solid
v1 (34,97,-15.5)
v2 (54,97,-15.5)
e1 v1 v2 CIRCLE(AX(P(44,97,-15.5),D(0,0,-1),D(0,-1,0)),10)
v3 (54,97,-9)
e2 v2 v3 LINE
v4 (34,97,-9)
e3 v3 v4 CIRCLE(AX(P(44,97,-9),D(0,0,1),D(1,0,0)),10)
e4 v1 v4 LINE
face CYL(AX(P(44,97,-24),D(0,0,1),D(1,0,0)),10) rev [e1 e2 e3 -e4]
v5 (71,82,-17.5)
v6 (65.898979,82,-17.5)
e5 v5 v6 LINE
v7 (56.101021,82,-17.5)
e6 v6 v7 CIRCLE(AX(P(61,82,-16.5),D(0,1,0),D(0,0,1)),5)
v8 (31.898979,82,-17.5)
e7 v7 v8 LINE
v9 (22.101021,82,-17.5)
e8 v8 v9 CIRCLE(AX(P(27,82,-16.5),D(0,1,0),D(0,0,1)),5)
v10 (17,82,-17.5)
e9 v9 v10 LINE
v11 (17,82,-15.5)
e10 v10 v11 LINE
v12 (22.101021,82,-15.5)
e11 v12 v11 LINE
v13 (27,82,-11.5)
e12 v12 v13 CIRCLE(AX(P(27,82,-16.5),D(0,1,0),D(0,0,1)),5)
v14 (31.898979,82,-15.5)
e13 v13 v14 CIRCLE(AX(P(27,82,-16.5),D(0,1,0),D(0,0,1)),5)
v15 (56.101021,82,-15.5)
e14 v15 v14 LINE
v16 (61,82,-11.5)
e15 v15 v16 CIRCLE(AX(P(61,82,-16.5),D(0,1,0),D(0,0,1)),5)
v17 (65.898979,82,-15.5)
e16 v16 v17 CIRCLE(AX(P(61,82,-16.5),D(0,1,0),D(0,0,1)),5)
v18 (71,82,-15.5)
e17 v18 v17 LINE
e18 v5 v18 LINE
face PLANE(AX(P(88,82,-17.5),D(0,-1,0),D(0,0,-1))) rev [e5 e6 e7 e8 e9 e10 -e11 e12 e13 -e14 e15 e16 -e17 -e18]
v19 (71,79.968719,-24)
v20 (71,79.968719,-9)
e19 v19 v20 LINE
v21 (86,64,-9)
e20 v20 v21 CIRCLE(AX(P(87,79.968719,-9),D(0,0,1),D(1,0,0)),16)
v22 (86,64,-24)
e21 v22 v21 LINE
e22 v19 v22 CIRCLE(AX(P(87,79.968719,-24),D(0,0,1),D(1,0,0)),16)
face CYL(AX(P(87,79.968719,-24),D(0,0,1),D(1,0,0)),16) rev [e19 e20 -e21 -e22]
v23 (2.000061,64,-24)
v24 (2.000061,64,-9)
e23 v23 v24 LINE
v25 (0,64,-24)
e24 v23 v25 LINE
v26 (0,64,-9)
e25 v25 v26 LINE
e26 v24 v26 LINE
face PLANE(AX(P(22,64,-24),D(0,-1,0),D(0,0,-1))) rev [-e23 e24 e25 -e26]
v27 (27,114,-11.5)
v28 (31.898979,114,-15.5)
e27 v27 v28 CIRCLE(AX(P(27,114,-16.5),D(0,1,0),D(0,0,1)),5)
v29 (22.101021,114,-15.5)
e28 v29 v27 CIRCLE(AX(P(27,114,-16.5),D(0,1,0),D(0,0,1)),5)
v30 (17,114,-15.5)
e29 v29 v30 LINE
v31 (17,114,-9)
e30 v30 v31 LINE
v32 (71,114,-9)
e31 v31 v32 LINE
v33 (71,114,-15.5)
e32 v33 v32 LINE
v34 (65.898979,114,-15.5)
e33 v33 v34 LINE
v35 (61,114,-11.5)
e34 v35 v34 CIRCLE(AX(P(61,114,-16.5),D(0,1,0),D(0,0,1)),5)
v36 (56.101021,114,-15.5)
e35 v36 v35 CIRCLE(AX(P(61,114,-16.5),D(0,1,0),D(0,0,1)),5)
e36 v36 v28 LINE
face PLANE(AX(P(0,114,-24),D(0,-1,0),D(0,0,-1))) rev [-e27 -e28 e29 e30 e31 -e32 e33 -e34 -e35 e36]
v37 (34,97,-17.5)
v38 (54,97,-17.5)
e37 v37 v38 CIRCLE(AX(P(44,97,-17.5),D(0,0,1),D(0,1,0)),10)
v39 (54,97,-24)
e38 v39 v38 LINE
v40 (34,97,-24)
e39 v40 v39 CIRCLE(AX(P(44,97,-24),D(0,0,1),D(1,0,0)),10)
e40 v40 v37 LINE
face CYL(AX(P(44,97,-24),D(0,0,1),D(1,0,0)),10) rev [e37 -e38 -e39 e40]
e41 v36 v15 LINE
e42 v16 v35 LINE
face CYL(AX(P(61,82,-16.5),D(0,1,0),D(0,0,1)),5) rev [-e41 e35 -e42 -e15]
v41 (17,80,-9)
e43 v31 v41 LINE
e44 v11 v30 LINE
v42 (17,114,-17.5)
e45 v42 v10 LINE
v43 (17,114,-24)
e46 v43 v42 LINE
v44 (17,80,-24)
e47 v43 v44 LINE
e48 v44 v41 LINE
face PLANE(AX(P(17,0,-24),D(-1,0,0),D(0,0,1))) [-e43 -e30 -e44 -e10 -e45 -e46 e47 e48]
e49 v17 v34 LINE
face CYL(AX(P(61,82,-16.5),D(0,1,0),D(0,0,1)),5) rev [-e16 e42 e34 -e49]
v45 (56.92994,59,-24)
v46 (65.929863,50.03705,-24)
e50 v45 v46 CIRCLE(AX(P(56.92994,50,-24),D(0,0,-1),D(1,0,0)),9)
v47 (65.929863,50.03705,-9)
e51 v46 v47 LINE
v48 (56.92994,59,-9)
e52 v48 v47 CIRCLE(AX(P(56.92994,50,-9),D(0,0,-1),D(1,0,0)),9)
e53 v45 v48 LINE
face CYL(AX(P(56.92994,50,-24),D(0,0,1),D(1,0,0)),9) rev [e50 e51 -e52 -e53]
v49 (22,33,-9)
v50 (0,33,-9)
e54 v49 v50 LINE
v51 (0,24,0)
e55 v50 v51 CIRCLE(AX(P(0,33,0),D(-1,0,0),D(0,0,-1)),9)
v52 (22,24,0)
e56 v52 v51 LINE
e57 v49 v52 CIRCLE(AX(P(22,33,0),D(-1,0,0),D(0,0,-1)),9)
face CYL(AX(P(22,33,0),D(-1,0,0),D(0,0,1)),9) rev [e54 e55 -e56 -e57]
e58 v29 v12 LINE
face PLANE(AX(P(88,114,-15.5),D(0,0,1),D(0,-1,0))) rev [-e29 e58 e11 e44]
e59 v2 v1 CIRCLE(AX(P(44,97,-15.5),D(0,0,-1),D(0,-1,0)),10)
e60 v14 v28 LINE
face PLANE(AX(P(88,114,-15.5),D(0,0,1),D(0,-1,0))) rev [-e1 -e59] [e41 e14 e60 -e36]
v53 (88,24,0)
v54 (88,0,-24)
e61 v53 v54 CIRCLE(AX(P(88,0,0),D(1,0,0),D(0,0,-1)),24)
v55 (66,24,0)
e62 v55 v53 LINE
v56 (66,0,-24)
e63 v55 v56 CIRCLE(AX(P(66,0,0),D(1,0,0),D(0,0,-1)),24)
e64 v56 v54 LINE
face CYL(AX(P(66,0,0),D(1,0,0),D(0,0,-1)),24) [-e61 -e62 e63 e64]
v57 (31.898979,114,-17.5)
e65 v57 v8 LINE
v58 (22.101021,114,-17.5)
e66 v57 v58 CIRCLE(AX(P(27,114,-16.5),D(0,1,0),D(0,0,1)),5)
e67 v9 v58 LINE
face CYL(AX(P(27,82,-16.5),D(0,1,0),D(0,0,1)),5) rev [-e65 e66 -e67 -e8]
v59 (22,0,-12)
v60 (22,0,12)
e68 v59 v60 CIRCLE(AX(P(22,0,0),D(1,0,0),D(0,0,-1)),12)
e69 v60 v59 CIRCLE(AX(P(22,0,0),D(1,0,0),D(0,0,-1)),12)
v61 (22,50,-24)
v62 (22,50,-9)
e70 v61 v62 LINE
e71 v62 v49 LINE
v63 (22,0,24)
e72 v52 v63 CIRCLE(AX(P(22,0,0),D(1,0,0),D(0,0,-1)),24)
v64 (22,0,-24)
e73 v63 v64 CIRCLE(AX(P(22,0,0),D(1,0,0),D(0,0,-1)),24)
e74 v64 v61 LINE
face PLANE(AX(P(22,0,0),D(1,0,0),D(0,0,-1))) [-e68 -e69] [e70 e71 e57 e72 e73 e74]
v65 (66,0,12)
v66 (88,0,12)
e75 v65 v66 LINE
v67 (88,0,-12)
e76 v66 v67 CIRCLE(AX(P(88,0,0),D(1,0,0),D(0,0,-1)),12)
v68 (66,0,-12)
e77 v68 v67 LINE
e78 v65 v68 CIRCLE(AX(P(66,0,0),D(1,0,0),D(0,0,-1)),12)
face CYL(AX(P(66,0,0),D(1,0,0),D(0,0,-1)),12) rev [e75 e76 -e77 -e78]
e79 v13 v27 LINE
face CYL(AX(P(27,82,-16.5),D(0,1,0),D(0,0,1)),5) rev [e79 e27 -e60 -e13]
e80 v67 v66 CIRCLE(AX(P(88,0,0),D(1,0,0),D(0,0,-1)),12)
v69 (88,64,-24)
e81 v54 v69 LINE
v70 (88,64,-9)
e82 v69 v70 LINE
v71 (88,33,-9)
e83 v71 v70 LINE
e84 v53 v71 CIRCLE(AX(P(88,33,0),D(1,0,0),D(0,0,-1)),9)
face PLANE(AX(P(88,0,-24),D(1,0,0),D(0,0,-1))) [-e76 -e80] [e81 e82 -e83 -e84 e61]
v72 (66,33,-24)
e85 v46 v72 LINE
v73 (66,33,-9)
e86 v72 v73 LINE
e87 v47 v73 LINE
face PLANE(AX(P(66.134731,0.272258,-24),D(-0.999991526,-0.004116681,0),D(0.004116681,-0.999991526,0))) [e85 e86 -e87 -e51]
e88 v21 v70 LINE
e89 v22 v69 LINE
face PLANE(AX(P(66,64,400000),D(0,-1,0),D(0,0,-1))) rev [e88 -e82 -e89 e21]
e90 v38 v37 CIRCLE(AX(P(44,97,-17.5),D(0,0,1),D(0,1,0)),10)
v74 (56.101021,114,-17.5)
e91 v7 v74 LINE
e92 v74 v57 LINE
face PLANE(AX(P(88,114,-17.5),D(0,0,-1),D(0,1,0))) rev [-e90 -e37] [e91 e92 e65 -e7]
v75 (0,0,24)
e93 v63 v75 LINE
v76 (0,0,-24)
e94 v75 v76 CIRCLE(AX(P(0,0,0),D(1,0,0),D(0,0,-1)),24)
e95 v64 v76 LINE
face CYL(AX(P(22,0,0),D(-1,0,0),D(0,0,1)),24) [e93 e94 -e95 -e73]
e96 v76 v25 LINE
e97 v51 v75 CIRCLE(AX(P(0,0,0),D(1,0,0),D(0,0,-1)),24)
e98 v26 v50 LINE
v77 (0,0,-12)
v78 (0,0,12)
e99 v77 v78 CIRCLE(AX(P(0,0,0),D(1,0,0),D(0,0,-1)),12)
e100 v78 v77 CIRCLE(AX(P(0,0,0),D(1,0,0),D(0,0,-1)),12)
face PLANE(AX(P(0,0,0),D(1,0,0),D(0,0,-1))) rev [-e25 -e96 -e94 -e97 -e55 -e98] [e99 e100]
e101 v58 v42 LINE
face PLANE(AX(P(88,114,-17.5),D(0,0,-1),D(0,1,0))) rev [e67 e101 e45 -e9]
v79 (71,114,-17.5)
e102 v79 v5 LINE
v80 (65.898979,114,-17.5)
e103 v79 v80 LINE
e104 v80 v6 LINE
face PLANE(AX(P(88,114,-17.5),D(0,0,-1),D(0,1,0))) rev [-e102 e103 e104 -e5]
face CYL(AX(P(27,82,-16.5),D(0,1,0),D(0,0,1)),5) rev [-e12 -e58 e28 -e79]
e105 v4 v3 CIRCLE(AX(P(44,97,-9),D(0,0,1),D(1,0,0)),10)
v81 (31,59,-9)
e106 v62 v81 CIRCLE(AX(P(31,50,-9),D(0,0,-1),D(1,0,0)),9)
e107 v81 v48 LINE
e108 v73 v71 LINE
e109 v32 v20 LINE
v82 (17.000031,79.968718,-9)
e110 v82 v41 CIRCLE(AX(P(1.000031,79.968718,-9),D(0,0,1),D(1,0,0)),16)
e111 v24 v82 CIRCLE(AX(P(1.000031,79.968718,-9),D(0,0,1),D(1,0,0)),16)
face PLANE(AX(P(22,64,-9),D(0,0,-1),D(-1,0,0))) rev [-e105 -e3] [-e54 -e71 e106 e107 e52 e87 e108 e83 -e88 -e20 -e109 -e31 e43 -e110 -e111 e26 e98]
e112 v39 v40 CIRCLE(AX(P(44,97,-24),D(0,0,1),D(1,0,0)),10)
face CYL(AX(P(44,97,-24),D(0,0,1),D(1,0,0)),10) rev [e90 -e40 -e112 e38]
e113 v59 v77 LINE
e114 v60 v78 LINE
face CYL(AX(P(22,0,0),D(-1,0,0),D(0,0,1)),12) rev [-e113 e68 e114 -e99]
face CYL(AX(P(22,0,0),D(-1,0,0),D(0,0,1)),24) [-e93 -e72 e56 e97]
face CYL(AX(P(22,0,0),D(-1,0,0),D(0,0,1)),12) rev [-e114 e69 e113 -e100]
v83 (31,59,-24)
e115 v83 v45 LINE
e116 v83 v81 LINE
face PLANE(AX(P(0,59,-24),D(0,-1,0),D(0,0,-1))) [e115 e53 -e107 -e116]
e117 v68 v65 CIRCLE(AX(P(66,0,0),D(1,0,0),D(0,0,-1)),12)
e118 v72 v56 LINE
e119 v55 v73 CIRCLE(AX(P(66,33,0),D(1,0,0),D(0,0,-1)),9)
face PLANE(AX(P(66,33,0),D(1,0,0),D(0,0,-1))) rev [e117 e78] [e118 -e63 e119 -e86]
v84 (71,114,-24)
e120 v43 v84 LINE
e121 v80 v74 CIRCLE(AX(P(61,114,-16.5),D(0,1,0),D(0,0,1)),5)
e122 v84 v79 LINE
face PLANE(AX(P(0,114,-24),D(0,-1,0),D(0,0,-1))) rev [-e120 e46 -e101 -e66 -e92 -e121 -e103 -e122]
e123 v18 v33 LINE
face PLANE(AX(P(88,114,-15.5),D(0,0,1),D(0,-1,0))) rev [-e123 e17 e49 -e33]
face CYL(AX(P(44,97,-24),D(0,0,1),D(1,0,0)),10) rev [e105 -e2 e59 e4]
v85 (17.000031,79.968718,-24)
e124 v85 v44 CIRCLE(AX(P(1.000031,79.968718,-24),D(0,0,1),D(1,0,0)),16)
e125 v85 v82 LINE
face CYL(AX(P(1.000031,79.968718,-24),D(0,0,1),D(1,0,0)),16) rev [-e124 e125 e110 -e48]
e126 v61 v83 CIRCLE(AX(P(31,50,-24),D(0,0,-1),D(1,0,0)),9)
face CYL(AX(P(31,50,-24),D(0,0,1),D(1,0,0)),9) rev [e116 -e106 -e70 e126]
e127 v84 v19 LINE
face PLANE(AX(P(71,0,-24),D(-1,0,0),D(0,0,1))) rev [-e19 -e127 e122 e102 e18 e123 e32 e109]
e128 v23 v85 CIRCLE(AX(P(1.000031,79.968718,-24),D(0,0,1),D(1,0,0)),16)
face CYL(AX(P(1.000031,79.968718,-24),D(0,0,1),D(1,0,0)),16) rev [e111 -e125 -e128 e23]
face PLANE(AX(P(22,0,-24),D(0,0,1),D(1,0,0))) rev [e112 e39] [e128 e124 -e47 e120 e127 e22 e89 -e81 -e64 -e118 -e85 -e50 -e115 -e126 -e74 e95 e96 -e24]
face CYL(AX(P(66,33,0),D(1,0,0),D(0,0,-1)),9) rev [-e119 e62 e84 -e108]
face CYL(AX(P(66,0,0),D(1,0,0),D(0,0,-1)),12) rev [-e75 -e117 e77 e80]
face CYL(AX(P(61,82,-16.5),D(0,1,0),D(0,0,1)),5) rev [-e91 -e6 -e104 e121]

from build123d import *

# Parameters (mm, degrees)
FORK_EYE_PROFILE_R         = 12
FORK_LEG_LEFT_DEPTH        = 22
FORK_START                 = 88
SKETCH1_4_R                = 12
FORK_LEG_RIGHT_DEPTH       = 22
CLAMP_BLOCK_DEPTH          = 15
CROSS_HOLE_SKETCH_R        = 10
CROSS_HOLE_DEPTH           = 15
CLAMP_SLIT_SKETCH_W        = 2
CLAMP_SLIT_SKETCH_H        = 32
CLAMP_SLIT_DEPTH           = 137.429468957
CLAMP_SCREW_HOLES_SKETCH_R = 5
CLAMP_SCREW_HOLES_DEPTH    = 32


with BuildPart() as part:
    # Fork Eye Profile → Fork Leg Left (new body)
    with BuildSketch(Plane(origin=(0, 0, 0), x_dir=(0, 0, -1), z_dir=(1, 0, 0))):
        with BuildLine():
            Line((24, 0), (24, 64))
            Line((24, 64), (9, 64))
            Line((9, 64), (9, 33))
            ThreePointArc((9, 33), (6.363961031, 26.636038969), (0, 24))
            ThreePointArc((0, 24), (-16.970562748, -16.970562748), (24, 0))
        make_face()
        Circle(FORK_EYE_PROFILE_R, mode=Mode.SUBTRACT)
    extrude(amount=FORK_LEG_LEFT_DEPTH)



with BuildPart() as body_2:
    # Sketch1_4 → Fork Leg Right (new body)
    with BuildSketch(Plane(origin=(0, 0, 0), x_dir=(0, 0, -1), z_dir=(1, 0, 0)).offset(FORK_START)):
        with BuildLine():
            Line((24, 0), (24, 64))
            Line((24, 64), (9, 64))
            Line((9, 64), (9, 33))
            ThreePointArc((9, 33), (6.363961031, 26.636038969), (0, 24))
            ThreePointArc((0, 24), (-16.970562748, -16.970562748), (24, 0))
        make_face()
        Circle(SKETCH1_4_R, mode=Mode.SUBTRACT)
    extrude(amount=-FORK_LEG_RIGHT_DEPTH)


with BuildPart() as part_1:
    add(part.part)

    add(body_2.part)  # Clamp Block merges body 2
    # Clamp Block Profile → Clamp Block (add)
    with BuildSketch(Plane.XY.offset(-9)):
        with BuildLine():
            Line((71, 114), (17, 114))
            Line((17, 114), (17, 80))
            ThreePointArc((17, 80), (12.672648111, 69.025683194), (2.000061163, 64))
            Line((2.000061163, 64), (22, 64))
            Line((22, 64), (22, 50))
            ThreePointArc((22, 50), (24.636038969, 56.363961031), (31, 59))
            Line((31, 59), (56.929939565, 59))
            ThreePointArc((56.929939565, 59), (63.280787887, 56.377046776), (65.929863303, 50.03705013))
            Line((65.929863303, 50.03705013), (66, 33))
            Line((66, 33), (88, 33))
            Line((88, 33), (88, 64))
            ThreePointArc((88, 64), (87, 63.968719423), (86, 64))
            ThreePointArc((86, 64), (75.33809621, 69.014268273), (71, 79.968719423))
            Line((71, 79.968719423), (71, 114))
        make_face()
        with BuildLine():
            Line((22, 64), (2.000061163, 64))
            ThreePointArc((2.000061163, 64), (1.000030581, 63.968717508), (0, 64))
            Line((0, 64), (0, 59))
            Line((0, 59), (0, 33))
            Line((0, 33), (22, 33))
            Line((22, 33), (22, 50))
            Line((22, 50), (22, 64))
        make_face()
    extrude(amount=-CLAMP_BLOCK_DEPTH)

    # Cross Hole Sketch → Cross Hole (cut)
    with BuildSketch(Plane.XY.offset(-9)):
        with Locations((44, 97)):
            Circle(CROSS_HOLE_SKETCH_R)
    extrude(amount=-CROSS_HOLE_DEPTH, mode=Mode.SUBTRACT)

    # Clamp Slit Sketch → Clamp Slit (cut, through all)
    with BuildSketch(Plane.ZY.offset(-17)):
        with Locations((-16.5, 98)):
            Rectangle(CLAMP_SLIT_SKETCH_W, CLAMP_SLIT_SKETCH_H)
    extrude(amount=-CLAMP_SLIT_DEPTH, mode=Mode.SUBTRACT)

    # Clamp Screw Holes Sketch → Clamp Screw Holes (cut)
    with BuildSketch(Plane(origin=(0, 114, 0), x_dir=(1, 0, 0), z_dir=(0, 1, 0))):
        with Locations((27, 16.5)):
            Circle(CLAMP_SCREW_HOLES_SKETCH_R)
        with Locations((61, 16.5)):
            Circle(CLAMP_SCREW_HOLES_SKETCH_R)
    extrude(amount=-CLAMP_SCREW_HOLES_DEPTH, mode=Mode.SUBTRACT)


solid = part_1.part
